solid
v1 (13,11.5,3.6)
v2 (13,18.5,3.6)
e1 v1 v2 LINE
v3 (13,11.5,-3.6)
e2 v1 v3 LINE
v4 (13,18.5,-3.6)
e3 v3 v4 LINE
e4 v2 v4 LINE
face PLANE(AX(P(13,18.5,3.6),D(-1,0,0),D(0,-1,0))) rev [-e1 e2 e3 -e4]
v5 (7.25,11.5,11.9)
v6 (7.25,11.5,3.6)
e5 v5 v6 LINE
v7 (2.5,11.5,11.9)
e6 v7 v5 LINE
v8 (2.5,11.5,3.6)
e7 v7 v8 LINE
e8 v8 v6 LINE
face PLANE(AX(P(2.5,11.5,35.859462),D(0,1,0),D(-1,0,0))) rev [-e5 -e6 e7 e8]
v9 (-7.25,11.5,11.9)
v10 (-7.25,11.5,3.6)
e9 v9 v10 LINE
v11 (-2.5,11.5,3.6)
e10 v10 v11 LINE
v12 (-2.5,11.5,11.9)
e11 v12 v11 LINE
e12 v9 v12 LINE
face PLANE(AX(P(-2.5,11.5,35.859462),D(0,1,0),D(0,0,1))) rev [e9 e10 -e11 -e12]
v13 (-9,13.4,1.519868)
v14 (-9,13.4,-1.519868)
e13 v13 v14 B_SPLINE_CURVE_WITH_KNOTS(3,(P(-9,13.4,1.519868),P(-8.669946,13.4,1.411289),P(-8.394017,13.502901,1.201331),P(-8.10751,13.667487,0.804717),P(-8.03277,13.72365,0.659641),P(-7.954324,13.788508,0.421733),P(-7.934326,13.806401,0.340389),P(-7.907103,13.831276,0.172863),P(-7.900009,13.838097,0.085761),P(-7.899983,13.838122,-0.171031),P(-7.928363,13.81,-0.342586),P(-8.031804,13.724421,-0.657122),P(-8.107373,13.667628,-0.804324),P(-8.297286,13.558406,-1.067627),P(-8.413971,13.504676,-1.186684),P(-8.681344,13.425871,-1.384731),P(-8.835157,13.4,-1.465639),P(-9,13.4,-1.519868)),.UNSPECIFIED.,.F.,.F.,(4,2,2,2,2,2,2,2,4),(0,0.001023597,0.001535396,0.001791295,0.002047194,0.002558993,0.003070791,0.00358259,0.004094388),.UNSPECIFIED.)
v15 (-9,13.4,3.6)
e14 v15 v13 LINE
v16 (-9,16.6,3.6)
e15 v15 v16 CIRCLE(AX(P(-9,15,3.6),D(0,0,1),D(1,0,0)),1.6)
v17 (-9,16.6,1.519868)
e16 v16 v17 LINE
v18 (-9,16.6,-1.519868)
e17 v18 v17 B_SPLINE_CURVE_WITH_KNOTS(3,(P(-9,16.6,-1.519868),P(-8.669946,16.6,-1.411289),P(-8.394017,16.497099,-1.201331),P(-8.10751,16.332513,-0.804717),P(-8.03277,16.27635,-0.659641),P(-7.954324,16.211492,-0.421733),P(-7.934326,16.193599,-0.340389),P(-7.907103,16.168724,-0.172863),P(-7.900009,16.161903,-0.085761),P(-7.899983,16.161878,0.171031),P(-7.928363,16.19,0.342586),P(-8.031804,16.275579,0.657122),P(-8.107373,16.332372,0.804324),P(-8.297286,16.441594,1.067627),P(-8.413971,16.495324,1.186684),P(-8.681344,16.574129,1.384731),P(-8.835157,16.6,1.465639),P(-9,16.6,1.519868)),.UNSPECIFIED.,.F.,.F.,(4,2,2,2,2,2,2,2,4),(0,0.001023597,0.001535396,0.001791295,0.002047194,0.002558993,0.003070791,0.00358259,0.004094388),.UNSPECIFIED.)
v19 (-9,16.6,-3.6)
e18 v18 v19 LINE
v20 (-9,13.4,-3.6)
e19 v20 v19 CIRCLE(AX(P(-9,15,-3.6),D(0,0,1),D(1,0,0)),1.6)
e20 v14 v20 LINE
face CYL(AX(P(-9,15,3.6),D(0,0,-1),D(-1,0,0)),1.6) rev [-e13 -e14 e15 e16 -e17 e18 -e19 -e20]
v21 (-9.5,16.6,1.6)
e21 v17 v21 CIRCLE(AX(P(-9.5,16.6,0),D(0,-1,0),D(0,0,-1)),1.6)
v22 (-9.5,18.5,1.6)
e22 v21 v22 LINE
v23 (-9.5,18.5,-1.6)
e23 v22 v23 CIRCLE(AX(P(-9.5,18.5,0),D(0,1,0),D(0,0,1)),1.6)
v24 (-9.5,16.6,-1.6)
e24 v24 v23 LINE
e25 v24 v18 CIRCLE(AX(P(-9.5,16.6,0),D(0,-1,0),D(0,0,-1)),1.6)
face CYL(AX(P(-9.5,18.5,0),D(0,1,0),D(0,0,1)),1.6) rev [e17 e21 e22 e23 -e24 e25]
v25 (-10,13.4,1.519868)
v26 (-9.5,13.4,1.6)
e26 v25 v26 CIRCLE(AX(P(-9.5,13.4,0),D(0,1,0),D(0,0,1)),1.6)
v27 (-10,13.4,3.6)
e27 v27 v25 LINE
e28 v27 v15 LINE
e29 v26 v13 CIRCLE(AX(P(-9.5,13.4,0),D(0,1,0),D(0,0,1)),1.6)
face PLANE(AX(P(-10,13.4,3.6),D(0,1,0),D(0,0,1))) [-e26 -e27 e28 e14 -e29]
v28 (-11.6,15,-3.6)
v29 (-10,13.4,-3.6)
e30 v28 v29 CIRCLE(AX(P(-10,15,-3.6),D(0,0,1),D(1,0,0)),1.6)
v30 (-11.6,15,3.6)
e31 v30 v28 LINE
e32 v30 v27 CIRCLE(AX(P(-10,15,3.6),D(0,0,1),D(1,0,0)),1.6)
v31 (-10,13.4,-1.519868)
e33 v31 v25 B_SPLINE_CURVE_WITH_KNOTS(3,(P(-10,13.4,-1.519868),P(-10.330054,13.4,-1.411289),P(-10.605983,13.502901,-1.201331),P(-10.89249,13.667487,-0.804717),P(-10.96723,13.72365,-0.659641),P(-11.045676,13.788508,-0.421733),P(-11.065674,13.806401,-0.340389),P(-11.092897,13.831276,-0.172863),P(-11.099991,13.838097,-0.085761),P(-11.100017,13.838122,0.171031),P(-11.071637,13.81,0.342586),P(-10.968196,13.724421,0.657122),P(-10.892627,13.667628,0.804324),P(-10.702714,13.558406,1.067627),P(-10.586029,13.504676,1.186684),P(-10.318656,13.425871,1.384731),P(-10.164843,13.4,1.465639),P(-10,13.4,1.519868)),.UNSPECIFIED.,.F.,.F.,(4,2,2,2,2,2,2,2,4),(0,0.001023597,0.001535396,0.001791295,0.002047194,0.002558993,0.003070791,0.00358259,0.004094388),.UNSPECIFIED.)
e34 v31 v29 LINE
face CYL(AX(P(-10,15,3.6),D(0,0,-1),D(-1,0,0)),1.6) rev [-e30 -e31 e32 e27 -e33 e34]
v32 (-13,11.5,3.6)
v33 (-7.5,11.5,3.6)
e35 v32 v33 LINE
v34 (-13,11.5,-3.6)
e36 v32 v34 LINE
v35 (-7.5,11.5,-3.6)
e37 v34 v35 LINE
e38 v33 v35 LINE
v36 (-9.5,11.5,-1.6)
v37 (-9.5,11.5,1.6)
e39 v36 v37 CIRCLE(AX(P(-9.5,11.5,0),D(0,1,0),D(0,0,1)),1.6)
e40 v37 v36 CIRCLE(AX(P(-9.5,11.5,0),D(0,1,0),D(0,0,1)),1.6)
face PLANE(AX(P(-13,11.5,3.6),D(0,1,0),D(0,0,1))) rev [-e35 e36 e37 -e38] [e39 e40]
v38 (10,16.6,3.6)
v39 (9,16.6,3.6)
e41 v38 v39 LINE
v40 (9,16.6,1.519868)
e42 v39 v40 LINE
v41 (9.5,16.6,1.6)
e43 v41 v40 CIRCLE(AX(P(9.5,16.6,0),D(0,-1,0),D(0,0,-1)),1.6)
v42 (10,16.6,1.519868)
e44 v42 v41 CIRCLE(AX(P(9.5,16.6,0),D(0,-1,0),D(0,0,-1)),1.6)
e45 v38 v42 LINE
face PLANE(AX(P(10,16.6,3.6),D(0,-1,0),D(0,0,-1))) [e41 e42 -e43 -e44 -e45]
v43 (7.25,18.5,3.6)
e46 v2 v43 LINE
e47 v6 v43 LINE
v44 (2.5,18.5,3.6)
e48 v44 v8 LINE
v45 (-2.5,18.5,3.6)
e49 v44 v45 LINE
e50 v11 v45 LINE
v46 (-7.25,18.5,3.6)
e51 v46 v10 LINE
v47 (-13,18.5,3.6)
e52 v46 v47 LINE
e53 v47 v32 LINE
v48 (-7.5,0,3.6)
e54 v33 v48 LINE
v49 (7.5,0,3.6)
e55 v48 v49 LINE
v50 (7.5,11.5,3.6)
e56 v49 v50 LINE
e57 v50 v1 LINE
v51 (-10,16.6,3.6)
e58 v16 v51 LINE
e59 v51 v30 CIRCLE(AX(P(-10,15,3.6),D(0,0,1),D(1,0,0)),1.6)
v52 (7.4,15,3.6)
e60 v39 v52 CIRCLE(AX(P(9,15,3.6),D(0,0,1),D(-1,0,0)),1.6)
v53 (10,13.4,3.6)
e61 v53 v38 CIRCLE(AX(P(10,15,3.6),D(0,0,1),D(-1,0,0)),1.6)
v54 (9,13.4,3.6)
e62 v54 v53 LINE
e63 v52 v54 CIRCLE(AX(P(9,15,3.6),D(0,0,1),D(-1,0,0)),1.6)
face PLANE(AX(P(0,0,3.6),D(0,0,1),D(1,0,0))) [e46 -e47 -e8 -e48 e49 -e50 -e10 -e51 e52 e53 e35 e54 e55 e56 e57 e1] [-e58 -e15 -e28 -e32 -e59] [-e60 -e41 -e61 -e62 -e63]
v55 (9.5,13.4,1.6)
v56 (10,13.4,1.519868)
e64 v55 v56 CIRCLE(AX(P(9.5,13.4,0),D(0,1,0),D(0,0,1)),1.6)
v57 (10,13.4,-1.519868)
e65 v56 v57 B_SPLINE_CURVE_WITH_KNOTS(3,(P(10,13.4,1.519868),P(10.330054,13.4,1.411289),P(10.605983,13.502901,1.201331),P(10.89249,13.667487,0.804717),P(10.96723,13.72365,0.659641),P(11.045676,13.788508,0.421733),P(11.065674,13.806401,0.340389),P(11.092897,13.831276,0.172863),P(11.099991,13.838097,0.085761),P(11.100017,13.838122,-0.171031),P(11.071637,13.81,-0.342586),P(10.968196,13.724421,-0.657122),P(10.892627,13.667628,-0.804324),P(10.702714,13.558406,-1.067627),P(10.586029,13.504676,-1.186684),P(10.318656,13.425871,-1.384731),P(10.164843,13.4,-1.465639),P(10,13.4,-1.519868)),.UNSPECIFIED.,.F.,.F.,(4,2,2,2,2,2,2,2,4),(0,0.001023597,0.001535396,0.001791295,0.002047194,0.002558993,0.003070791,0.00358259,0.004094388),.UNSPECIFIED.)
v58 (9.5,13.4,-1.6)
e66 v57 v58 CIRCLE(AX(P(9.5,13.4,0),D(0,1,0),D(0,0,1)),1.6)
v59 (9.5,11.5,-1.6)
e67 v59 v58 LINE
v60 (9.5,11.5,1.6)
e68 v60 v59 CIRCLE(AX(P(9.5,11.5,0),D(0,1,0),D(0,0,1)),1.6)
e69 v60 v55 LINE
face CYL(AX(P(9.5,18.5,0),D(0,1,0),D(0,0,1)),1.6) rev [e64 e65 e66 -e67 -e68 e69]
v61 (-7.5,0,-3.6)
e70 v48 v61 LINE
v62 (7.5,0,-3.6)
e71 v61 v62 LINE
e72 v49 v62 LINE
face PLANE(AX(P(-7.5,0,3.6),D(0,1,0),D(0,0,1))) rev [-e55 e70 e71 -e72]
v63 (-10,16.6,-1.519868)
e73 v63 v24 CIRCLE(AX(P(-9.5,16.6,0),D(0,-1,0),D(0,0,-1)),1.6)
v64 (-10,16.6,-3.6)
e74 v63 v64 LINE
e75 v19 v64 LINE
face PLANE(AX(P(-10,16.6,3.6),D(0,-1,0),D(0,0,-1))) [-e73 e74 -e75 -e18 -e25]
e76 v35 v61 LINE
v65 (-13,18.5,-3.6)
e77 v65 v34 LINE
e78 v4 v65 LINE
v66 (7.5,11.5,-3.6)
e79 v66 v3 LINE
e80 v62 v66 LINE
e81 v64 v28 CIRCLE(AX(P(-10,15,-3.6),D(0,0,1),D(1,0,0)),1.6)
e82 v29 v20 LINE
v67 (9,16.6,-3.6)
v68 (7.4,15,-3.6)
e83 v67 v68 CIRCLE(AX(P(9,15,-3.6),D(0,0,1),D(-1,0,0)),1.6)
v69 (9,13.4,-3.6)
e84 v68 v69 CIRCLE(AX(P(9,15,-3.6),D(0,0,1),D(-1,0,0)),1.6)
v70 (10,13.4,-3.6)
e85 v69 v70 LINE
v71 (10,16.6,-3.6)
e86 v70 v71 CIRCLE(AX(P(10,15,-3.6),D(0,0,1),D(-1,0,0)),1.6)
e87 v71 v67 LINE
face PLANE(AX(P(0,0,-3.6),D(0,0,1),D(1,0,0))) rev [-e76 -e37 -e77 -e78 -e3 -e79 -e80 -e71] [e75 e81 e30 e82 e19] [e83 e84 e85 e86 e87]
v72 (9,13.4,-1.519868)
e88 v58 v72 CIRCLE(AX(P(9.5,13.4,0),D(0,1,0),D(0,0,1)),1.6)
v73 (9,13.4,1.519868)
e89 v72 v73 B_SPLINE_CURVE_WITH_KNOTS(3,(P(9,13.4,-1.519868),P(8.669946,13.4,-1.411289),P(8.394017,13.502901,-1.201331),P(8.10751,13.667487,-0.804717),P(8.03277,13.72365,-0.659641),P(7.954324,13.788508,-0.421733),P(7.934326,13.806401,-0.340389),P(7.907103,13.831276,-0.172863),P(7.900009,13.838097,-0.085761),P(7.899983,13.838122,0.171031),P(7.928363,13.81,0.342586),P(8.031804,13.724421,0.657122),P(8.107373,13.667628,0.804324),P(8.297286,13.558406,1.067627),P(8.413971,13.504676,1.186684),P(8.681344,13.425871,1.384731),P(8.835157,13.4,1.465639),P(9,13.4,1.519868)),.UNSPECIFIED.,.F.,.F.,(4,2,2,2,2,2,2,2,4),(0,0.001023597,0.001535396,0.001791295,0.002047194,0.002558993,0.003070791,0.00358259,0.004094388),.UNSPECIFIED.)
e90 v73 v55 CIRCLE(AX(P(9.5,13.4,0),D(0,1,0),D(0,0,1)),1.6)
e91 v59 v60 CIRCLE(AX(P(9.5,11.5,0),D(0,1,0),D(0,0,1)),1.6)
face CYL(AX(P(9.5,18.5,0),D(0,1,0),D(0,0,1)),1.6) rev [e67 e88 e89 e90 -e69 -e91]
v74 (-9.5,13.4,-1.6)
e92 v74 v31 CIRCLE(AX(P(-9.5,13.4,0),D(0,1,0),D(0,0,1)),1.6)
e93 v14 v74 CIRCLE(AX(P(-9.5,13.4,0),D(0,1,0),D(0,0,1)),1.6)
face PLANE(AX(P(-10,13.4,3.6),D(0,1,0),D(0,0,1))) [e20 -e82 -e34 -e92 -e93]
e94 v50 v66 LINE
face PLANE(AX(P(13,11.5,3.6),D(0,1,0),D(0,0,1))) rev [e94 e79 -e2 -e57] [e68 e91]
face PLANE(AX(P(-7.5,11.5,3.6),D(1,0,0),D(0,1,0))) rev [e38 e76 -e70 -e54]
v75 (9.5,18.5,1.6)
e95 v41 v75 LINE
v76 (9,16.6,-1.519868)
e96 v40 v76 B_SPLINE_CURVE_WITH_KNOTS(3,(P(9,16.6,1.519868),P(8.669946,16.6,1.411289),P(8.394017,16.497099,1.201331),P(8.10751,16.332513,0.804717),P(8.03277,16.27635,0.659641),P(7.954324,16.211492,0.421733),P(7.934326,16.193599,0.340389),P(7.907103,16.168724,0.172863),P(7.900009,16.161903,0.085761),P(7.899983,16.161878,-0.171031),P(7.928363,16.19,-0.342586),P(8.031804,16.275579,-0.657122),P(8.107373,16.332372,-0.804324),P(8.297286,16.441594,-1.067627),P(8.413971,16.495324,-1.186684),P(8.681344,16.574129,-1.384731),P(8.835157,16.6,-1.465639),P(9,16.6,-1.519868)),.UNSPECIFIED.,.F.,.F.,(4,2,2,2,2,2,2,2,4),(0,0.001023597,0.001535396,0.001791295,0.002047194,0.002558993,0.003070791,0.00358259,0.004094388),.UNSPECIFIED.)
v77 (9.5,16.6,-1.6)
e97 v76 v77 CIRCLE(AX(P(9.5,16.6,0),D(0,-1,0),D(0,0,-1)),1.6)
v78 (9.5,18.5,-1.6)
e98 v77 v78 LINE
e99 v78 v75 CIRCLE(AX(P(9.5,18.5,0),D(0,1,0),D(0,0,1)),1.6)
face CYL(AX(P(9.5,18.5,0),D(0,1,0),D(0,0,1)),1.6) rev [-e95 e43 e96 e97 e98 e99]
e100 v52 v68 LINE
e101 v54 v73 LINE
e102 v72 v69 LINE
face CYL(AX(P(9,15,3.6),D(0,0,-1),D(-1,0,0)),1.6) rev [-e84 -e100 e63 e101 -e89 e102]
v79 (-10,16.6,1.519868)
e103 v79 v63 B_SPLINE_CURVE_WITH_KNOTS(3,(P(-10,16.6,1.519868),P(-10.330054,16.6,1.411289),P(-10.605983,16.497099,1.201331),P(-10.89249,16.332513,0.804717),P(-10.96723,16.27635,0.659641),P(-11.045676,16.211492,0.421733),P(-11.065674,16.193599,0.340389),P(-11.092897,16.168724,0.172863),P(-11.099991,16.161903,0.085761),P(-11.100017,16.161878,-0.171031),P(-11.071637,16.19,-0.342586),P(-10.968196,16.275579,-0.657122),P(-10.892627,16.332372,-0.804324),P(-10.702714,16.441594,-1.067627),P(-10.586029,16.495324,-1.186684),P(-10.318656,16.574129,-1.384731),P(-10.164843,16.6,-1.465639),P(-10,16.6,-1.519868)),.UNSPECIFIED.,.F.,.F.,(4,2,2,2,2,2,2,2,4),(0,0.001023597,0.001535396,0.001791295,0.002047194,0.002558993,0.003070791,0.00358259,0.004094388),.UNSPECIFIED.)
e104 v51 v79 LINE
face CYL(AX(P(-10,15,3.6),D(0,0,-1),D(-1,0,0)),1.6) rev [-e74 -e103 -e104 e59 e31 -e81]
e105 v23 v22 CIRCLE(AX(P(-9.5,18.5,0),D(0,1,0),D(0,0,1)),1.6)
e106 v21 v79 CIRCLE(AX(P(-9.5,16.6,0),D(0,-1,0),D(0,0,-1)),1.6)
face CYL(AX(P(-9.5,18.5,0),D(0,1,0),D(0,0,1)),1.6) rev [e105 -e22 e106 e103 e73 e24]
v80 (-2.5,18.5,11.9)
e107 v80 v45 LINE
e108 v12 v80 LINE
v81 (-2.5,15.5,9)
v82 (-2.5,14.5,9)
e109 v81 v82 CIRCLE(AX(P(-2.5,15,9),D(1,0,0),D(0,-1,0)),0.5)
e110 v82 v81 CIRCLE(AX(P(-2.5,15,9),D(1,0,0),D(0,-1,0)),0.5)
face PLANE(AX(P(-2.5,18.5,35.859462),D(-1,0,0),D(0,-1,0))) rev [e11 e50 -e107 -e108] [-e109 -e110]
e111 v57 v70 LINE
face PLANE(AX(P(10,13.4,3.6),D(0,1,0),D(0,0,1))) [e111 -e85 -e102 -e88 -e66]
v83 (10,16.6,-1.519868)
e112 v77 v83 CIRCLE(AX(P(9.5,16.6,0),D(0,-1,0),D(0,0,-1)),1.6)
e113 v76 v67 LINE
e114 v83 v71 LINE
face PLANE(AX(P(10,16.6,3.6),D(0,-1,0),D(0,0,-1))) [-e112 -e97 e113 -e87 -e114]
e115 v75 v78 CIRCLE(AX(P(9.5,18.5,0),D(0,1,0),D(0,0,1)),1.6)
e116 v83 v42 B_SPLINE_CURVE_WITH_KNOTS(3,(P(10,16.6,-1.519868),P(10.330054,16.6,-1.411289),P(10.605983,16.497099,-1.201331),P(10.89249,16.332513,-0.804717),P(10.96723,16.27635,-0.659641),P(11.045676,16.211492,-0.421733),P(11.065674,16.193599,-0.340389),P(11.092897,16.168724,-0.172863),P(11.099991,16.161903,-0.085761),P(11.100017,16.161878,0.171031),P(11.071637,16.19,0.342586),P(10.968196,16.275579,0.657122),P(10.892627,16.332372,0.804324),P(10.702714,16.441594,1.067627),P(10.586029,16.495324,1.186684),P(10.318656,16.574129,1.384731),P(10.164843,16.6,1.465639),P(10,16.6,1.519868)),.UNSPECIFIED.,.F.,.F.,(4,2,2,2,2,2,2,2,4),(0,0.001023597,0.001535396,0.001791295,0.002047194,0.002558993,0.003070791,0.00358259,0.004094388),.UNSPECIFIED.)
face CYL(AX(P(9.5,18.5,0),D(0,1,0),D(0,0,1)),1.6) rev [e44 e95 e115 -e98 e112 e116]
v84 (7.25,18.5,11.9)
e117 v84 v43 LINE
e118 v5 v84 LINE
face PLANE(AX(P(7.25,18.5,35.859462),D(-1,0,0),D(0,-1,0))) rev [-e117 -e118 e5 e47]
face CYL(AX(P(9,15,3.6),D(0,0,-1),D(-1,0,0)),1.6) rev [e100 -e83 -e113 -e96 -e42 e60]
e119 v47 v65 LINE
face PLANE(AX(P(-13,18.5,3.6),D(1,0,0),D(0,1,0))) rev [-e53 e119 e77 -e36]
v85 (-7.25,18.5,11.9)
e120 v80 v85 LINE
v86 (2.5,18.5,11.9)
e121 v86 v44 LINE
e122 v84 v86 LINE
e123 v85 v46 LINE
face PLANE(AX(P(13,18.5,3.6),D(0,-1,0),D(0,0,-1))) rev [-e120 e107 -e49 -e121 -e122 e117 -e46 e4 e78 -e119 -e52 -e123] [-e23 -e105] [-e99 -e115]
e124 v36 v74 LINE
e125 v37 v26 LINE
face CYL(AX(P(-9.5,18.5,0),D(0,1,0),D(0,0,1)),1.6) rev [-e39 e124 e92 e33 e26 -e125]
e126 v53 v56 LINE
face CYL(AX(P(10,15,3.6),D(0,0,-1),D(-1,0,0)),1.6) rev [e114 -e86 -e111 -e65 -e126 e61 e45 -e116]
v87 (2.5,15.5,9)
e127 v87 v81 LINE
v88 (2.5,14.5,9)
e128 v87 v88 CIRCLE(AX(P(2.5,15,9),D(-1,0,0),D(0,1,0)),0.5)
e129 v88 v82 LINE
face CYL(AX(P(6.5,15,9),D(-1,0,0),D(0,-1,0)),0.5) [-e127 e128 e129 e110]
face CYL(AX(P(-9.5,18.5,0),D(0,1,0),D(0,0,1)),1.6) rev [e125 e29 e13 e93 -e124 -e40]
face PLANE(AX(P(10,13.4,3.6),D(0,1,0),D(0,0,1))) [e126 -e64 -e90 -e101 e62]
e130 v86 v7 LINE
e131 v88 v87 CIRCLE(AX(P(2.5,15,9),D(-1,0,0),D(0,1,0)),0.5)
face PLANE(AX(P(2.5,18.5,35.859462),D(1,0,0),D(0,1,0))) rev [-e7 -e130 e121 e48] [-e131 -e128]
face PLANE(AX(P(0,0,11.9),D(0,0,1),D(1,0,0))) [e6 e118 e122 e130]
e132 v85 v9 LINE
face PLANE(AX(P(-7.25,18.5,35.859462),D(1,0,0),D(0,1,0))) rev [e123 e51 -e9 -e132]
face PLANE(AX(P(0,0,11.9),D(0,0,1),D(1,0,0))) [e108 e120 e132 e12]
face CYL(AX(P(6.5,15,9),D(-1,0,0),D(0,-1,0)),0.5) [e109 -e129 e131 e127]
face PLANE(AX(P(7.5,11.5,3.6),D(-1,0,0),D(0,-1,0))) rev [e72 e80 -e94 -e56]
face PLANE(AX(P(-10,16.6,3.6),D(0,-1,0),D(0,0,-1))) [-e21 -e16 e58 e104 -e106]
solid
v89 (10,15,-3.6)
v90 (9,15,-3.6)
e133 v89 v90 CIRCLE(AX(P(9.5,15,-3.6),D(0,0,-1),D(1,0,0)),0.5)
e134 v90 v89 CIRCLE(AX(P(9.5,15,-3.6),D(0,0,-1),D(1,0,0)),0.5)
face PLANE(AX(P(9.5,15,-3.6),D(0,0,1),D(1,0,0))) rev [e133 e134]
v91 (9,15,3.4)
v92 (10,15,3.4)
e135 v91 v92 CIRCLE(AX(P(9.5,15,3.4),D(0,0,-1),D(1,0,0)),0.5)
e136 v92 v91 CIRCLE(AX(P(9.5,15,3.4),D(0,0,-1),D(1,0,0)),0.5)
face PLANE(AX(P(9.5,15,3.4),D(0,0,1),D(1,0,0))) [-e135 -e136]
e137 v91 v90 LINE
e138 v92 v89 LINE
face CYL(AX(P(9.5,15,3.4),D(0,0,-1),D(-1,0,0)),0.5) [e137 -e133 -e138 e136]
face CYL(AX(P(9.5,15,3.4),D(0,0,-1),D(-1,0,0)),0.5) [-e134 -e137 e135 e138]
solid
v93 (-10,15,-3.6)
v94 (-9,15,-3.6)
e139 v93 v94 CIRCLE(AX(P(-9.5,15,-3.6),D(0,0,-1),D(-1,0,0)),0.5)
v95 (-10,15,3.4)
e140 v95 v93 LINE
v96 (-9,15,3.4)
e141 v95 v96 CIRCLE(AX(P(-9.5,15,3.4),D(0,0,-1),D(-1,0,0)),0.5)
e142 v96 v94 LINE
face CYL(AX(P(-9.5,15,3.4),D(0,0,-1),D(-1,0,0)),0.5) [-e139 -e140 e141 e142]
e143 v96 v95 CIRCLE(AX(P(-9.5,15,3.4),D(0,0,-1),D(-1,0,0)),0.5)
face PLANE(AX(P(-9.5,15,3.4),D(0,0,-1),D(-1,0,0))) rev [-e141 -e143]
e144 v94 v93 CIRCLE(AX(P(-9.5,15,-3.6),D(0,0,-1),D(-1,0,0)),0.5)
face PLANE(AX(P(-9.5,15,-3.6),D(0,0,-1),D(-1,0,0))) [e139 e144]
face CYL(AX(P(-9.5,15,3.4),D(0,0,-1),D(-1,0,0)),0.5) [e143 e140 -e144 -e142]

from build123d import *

# Parameters (mm, degrees)
EXTRUDE_1_DEPTH         = 3.6
SKETCH_2_W              = 4.75
SKETCH_2_H              = 7
EXTRUDE_2_DEPTH         = 8.3
SKETCH_3_R              = 0.5
EXTRUDE_3_DEPTH         = 9
HOLE_WIZARD_3_2_3_2_1_D = 3.2
SKETCH_4_R              = 0.5
EXTRUDE_4_DEPTH         = 7
EXTRUDE_4_2_DEPTH       = 7


with BuildPart() as part:
    # 草图1 → 凸台-拉伸1 (new, symmetric)
    with BuildSketch(Plane.XY):
        Polygon((13, 18.5), (-13, 18.5), (-13, 11.5), (-7.5, 11.5), (-7.5, 0), (7.5, 0), (7.5, 11.5), (13, 11.5), align=None)
        with BuildLine():
            Line((-10, 16.6), (-9, 16.6))
            ThreePointArc((-9, 16.6), (-7.4, 15), (-9, 13.4))
            Line((-9, 13.4), (-10, 13.4))
            ThreePointArc((-10, 13.4), (-11.6, 15), (-10, 16.6))
        make_face(mode=Mode.SUBTRACT)
        with BuildLine():
            Line((10, 16.6), (9, 16.6))
            ThreePointArc((9, 16.6), (7.4, 15), (9, 13.4))
            Line((9, 13.4), (10, 13.4))
            ThreePointArc((10, 13.4), (11.6, 15), (10, 16.6))
        make_face(mode=Mode.SUBTRACT)
    extrude(amount=EXTRUDE_1_DEPTH, both=True)

    # 草图2 → 凸台-拉伸2 (add)
    with BuildSketch(Plane.XY.offset(3.6)):
        with Locations((-4.875, 15)):
            Rectangle(SKETCH_2_W, SKETCH_2_H)
        with Locations((4.875, 15)):
            Rectangle(SKETCH_2_W, SKETCH_2_H)
    extrude(amount=EXTRUDE_2_DEPTH)

    # 草图3 → 凸台-拉伸3 (add)
    with BuildSketch(Plane(origin=(-2.5, 0, 0), x_dir=(0, 0, -1), z_dir=(1, 0, 0))):
        with Locations(Location((-9, 15, 0), (0, 0, 270))):
            Circle(SKETCH_3_R)
    extrude(amount=EXTRUDE_3_DEPTH)

    # Ø3.2 (3.2) 直径孔1 (through all)
    with Locations(Plane(origin=(0, 18.5, 0), x_dir=(1, 0, 0), z_dir=(0, 1, 0))):
        with Locations((-9.5, 0), (9.5, 0)):
            Hole(HOLE_WIZARD_3_2_3_2_1_D / 2)


with BuildPart() as body_2:
    # 草图4 → 凸台-拉伸4 (new body)
    with BuildSketch(Plane(origin=(0, 0, -3.6), x_dir=(-1, 0, 0), z_dir=(0, 0, -1))):
        with Locations((9.5, 15)):
            Circle(SKETCH_4_R)
    extrude(amount=-EXTRUDE_4_DEPTH)


with BuildPart() as body_3:
    # 草图4 → Extrude 4 2 (new body)
    with BuildSketch(Plane(origin=(0, 0, -3.6), x_dir=(-1, 0, 0), z_dir=(0, 0, -1))):
        with Locations(Location((-9.5, 15, 0), (0, 0, 180))):
            Circle(SKETCH_4_R)
    extrude(amount=-EXTRUDE_4_2_DEPTH)


solid = Compound([part.part, body_2.part, body_3.part])
